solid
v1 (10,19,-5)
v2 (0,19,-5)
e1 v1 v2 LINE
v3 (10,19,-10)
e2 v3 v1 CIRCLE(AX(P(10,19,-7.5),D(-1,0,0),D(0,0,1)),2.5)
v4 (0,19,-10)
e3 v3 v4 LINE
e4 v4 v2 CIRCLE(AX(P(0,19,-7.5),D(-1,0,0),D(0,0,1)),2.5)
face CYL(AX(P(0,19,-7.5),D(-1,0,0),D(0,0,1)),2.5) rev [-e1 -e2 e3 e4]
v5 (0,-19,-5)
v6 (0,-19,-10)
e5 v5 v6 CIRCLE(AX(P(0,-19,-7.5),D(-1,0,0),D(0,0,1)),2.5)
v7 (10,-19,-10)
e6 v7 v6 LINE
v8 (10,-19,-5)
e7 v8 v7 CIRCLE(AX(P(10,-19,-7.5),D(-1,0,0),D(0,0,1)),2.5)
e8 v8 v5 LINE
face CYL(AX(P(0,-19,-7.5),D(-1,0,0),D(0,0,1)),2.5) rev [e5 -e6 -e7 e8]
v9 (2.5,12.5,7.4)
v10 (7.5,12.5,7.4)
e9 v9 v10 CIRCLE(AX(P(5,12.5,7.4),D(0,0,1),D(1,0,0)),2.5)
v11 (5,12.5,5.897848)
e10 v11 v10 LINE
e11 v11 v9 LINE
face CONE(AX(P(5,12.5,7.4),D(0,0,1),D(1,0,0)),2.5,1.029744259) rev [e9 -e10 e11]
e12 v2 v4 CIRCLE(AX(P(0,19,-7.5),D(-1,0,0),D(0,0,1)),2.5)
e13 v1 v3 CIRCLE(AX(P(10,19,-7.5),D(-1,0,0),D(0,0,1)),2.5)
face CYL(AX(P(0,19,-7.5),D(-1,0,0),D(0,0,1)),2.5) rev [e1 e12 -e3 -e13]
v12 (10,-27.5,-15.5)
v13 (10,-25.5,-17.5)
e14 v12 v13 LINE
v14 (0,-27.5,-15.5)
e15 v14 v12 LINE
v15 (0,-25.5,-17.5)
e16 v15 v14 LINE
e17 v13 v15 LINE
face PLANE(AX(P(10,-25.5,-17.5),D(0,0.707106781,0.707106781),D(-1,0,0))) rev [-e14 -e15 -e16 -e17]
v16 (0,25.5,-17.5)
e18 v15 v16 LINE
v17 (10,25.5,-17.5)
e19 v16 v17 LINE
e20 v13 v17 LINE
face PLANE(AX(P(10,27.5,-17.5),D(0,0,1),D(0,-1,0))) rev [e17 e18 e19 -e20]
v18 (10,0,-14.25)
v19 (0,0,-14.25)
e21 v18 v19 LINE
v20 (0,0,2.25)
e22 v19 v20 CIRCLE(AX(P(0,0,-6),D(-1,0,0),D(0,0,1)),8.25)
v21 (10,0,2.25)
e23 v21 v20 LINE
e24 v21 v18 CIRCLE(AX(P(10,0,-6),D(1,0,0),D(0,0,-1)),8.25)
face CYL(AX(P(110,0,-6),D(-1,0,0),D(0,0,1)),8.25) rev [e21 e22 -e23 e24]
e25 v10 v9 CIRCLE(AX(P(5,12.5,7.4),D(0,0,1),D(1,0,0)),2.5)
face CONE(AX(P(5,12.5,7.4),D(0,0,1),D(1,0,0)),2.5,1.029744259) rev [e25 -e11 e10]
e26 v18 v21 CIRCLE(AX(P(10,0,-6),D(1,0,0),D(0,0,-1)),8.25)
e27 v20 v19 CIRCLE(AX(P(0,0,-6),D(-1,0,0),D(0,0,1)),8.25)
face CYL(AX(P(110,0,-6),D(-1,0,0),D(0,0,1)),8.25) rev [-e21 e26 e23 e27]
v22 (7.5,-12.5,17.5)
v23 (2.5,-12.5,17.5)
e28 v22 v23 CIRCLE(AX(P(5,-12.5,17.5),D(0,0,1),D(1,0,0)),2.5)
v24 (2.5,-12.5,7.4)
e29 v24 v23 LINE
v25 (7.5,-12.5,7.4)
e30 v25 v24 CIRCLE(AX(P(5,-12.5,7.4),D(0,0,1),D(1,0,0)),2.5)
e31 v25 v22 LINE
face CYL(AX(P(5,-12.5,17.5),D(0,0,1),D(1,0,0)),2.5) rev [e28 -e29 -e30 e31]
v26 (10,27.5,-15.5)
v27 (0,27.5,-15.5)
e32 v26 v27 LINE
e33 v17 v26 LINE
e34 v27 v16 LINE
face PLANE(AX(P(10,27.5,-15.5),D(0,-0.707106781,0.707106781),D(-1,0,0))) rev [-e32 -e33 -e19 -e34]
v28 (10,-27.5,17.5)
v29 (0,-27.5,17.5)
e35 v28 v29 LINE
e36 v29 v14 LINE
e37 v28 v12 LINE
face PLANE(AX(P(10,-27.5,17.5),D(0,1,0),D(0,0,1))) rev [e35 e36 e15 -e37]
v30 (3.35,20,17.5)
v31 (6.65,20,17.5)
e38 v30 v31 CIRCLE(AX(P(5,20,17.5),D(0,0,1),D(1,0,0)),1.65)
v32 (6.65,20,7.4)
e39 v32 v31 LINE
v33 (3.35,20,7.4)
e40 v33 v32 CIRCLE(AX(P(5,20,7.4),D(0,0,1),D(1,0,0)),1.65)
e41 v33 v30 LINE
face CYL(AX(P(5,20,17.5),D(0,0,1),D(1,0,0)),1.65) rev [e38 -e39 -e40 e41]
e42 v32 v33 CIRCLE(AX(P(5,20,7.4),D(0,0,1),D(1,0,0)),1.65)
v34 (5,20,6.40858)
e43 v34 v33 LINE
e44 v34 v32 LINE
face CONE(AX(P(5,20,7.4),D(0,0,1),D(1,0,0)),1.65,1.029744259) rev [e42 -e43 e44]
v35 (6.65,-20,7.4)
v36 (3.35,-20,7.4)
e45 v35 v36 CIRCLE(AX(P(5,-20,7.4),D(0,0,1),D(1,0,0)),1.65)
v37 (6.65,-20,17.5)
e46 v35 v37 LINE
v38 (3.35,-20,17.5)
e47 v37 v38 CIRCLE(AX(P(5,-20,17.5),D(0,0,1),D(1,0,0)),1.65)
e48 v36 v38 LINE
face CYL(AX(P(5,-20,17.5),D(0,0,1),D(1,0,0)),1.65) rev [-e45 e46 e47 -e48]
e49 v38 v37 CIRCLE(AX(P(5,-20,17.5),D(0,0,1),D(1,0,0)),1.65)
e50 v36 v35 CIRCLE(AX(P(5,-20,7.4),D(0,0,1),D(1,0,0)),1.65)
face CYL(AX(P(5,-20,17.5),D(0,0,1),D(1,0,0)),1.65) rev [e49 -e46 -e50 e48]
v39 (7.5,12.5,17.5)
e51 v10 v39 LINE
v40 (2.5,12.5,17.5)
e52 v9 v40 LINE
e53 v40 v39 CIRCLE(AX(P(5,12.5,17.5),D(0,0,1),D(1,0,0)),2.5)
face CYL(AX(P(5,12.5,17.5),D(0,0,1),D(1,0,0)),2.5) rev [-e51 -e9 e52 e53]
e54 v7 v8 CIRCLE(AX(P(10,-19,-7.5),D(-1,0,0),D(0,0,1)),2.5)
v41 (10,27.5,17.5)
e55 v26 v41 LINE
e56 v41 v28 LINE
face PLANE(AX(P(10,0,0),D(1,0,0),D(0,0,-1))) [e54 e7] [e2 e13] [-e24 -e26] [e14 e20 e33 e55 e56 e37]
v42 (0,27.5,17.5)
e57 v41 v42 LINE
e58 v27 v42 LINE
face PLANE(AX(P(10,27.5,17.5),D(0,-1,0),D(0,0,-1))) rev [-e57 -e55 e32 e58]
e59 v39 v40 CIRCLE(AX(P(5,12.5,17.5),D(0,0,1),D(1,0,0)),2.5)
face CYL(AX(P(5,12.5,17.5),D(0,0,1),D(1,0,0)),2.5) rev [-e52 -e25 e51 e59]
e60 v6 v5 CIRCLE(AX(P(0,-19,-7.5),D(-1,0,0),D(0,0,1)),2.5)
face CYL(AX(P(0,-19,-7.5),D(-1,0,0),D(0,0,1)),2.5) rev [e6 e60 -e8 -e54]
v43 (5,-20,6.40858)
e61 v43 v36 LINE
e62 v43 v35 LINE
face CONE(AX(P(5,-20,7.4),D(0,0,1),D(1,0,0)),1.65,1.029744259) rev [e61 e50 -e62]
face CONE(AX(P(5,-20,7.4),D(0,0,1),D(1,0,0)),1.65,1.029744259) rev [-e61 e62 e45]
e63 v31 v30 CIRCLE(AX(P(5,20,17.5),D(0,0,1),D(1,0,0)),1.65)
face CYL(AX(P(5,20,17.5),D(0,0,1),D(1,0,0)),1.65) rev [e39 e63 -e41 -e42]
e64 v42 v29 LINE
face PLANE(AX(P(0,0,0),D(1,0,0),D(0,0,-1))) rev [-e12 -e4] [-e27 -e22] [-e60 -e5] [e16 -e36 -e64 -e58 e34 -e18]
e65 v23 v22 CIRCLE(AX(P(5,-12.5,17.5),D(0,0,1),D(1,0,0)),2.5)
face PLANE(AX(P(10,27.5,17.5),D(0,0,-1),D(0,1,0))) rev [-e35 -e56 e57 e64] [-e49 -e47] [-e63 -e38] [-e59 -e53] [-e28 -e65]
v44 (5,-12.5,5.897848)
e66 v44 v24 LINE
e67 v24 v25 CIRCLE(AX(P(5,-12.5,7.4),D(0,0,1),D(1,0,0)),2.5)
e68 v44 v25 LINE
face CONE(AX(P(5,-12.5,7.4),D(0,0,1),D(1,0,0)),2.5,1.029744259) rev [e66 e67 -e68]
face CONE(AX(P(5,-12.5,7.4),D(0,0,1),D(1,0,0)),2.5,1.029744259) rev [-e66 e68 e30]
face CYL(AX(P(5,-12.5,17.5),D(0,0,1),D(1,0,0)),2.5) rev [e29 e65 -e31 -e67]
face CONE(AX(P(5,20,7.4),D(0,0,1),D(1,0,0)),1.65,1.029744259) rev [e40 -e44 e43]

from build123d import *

# Parameters (mm, degrees)
SKETCH_1_W                = 35
SKETCH_1_H                = 55
EXTRUDE_1_DEPTH           = 10
SKETCH_2_R                = 8.25
CUT_EXTRUDE_1_DEPTH       = 110
HOLE_WIZARD_M6_1_D        = 5
HOLE_WIZARD_M4_1_D        = 3.3
HOLE_WIZARD_M4_1_DEPTH    = 10.1
HOLE_WIZARD_M4_1_TIP      = 0.991420021
HOLE_WIZARD_5_0_5_1_D     = 5
HOLE_WIZARD_5_0_5_1_DEPTH = 10.1
HOLE_WIZARD_5_0_5_1_TIP   = 1.502151548
CHAMFER_1_SIZE            = 2


with BuildPart() as part:
    # 草图1 → 凸台-拉伸1 (new body)
    with BuildSketch(Plane(origin=(0, 0, 0), x_dir=(0, 0, -1), z_dir=(1, 0, 0))):
        Rectangle(SKETCH_1_W, SKETCH_1_H)
    extrude(amount=EXTRUDE_1_DEPTH)

    # 草图2 → 切除-拉伸1 (cut)
    with BuildSketch(Plane.ZY):
        with Locations((-6, 0)):
            Circle(SKETCH_2_R)
    extrude(amount=-CUT_EXTRUDE_1_DEPTH, mode=Mode.SUBTRACT)

    # M6 螺纹孔1 (through all)
    with Locations(Plane.ZY):
        with Locations((-7.5, -19)):
            hole_wizard_m6_1 = Hole(HOLE_WIZARD_M6_1_D / 2)

    # 镜向1: M6 螺纹孔1 across plane
    add(hole_wizard_m6_1.mirror(Plane.ZX), mode=Mode.SUBTRACT)

    # M4 螺纹孔1
    with Locations(Plane.XY.offset(17.5)):
        with Locations((5, 20), (5, -20)):
            Hole(HOLE_WIZARD_M4_1_D / 2, depth=HOLE_WIZARD_M4_1_DEPTH)
            with Locations((0, 0, -(HOLE_WIZARD_M4_1_DEPTH + HOLE_WIZARD_M4_1_TIP / 2))):  # 118° drill point
                Cone(0, HOLE_WIZARD_M4_1_D / 2, HOLE_WIZARD_M4_1_TIP, mode=Mode.SUBTRACT)

    # Ø5.0 (5) 直径孔1
    with Locations(Plane.XY.offset(17.5)):
        with Locations((5, 12.5), (5, -12.5)):
            Hole(HOLE_WIZARD_5_0_5_1_D / 2, depth=HOLE_WIZARD_5_0_5_1_DEPTH)
            with Locations((0, 0, -(HOLE_WIZARD_5_0_5_1_DEPTH + HOLE_WIZARD_5_0_5_1_TIP / 2))):  # 118° drill point
                Cone(0, HOLE_WIZARD_5_0_5_1_D / 2, HOLE_WIZARD_5_0_5_1_TIP, mode=Mode.SUBTRACT)

    # 倒角1
    chamfer_1_edges = [part.edges().sort_by_distance(p)[0] for p in [
        (5, -27.5, -17.5),
        (5, 27.5, -17.5),
    ]]
    chamfer(chamfer_1_edges, length=CHAMFER_1_SIZE)


solid = part.part
